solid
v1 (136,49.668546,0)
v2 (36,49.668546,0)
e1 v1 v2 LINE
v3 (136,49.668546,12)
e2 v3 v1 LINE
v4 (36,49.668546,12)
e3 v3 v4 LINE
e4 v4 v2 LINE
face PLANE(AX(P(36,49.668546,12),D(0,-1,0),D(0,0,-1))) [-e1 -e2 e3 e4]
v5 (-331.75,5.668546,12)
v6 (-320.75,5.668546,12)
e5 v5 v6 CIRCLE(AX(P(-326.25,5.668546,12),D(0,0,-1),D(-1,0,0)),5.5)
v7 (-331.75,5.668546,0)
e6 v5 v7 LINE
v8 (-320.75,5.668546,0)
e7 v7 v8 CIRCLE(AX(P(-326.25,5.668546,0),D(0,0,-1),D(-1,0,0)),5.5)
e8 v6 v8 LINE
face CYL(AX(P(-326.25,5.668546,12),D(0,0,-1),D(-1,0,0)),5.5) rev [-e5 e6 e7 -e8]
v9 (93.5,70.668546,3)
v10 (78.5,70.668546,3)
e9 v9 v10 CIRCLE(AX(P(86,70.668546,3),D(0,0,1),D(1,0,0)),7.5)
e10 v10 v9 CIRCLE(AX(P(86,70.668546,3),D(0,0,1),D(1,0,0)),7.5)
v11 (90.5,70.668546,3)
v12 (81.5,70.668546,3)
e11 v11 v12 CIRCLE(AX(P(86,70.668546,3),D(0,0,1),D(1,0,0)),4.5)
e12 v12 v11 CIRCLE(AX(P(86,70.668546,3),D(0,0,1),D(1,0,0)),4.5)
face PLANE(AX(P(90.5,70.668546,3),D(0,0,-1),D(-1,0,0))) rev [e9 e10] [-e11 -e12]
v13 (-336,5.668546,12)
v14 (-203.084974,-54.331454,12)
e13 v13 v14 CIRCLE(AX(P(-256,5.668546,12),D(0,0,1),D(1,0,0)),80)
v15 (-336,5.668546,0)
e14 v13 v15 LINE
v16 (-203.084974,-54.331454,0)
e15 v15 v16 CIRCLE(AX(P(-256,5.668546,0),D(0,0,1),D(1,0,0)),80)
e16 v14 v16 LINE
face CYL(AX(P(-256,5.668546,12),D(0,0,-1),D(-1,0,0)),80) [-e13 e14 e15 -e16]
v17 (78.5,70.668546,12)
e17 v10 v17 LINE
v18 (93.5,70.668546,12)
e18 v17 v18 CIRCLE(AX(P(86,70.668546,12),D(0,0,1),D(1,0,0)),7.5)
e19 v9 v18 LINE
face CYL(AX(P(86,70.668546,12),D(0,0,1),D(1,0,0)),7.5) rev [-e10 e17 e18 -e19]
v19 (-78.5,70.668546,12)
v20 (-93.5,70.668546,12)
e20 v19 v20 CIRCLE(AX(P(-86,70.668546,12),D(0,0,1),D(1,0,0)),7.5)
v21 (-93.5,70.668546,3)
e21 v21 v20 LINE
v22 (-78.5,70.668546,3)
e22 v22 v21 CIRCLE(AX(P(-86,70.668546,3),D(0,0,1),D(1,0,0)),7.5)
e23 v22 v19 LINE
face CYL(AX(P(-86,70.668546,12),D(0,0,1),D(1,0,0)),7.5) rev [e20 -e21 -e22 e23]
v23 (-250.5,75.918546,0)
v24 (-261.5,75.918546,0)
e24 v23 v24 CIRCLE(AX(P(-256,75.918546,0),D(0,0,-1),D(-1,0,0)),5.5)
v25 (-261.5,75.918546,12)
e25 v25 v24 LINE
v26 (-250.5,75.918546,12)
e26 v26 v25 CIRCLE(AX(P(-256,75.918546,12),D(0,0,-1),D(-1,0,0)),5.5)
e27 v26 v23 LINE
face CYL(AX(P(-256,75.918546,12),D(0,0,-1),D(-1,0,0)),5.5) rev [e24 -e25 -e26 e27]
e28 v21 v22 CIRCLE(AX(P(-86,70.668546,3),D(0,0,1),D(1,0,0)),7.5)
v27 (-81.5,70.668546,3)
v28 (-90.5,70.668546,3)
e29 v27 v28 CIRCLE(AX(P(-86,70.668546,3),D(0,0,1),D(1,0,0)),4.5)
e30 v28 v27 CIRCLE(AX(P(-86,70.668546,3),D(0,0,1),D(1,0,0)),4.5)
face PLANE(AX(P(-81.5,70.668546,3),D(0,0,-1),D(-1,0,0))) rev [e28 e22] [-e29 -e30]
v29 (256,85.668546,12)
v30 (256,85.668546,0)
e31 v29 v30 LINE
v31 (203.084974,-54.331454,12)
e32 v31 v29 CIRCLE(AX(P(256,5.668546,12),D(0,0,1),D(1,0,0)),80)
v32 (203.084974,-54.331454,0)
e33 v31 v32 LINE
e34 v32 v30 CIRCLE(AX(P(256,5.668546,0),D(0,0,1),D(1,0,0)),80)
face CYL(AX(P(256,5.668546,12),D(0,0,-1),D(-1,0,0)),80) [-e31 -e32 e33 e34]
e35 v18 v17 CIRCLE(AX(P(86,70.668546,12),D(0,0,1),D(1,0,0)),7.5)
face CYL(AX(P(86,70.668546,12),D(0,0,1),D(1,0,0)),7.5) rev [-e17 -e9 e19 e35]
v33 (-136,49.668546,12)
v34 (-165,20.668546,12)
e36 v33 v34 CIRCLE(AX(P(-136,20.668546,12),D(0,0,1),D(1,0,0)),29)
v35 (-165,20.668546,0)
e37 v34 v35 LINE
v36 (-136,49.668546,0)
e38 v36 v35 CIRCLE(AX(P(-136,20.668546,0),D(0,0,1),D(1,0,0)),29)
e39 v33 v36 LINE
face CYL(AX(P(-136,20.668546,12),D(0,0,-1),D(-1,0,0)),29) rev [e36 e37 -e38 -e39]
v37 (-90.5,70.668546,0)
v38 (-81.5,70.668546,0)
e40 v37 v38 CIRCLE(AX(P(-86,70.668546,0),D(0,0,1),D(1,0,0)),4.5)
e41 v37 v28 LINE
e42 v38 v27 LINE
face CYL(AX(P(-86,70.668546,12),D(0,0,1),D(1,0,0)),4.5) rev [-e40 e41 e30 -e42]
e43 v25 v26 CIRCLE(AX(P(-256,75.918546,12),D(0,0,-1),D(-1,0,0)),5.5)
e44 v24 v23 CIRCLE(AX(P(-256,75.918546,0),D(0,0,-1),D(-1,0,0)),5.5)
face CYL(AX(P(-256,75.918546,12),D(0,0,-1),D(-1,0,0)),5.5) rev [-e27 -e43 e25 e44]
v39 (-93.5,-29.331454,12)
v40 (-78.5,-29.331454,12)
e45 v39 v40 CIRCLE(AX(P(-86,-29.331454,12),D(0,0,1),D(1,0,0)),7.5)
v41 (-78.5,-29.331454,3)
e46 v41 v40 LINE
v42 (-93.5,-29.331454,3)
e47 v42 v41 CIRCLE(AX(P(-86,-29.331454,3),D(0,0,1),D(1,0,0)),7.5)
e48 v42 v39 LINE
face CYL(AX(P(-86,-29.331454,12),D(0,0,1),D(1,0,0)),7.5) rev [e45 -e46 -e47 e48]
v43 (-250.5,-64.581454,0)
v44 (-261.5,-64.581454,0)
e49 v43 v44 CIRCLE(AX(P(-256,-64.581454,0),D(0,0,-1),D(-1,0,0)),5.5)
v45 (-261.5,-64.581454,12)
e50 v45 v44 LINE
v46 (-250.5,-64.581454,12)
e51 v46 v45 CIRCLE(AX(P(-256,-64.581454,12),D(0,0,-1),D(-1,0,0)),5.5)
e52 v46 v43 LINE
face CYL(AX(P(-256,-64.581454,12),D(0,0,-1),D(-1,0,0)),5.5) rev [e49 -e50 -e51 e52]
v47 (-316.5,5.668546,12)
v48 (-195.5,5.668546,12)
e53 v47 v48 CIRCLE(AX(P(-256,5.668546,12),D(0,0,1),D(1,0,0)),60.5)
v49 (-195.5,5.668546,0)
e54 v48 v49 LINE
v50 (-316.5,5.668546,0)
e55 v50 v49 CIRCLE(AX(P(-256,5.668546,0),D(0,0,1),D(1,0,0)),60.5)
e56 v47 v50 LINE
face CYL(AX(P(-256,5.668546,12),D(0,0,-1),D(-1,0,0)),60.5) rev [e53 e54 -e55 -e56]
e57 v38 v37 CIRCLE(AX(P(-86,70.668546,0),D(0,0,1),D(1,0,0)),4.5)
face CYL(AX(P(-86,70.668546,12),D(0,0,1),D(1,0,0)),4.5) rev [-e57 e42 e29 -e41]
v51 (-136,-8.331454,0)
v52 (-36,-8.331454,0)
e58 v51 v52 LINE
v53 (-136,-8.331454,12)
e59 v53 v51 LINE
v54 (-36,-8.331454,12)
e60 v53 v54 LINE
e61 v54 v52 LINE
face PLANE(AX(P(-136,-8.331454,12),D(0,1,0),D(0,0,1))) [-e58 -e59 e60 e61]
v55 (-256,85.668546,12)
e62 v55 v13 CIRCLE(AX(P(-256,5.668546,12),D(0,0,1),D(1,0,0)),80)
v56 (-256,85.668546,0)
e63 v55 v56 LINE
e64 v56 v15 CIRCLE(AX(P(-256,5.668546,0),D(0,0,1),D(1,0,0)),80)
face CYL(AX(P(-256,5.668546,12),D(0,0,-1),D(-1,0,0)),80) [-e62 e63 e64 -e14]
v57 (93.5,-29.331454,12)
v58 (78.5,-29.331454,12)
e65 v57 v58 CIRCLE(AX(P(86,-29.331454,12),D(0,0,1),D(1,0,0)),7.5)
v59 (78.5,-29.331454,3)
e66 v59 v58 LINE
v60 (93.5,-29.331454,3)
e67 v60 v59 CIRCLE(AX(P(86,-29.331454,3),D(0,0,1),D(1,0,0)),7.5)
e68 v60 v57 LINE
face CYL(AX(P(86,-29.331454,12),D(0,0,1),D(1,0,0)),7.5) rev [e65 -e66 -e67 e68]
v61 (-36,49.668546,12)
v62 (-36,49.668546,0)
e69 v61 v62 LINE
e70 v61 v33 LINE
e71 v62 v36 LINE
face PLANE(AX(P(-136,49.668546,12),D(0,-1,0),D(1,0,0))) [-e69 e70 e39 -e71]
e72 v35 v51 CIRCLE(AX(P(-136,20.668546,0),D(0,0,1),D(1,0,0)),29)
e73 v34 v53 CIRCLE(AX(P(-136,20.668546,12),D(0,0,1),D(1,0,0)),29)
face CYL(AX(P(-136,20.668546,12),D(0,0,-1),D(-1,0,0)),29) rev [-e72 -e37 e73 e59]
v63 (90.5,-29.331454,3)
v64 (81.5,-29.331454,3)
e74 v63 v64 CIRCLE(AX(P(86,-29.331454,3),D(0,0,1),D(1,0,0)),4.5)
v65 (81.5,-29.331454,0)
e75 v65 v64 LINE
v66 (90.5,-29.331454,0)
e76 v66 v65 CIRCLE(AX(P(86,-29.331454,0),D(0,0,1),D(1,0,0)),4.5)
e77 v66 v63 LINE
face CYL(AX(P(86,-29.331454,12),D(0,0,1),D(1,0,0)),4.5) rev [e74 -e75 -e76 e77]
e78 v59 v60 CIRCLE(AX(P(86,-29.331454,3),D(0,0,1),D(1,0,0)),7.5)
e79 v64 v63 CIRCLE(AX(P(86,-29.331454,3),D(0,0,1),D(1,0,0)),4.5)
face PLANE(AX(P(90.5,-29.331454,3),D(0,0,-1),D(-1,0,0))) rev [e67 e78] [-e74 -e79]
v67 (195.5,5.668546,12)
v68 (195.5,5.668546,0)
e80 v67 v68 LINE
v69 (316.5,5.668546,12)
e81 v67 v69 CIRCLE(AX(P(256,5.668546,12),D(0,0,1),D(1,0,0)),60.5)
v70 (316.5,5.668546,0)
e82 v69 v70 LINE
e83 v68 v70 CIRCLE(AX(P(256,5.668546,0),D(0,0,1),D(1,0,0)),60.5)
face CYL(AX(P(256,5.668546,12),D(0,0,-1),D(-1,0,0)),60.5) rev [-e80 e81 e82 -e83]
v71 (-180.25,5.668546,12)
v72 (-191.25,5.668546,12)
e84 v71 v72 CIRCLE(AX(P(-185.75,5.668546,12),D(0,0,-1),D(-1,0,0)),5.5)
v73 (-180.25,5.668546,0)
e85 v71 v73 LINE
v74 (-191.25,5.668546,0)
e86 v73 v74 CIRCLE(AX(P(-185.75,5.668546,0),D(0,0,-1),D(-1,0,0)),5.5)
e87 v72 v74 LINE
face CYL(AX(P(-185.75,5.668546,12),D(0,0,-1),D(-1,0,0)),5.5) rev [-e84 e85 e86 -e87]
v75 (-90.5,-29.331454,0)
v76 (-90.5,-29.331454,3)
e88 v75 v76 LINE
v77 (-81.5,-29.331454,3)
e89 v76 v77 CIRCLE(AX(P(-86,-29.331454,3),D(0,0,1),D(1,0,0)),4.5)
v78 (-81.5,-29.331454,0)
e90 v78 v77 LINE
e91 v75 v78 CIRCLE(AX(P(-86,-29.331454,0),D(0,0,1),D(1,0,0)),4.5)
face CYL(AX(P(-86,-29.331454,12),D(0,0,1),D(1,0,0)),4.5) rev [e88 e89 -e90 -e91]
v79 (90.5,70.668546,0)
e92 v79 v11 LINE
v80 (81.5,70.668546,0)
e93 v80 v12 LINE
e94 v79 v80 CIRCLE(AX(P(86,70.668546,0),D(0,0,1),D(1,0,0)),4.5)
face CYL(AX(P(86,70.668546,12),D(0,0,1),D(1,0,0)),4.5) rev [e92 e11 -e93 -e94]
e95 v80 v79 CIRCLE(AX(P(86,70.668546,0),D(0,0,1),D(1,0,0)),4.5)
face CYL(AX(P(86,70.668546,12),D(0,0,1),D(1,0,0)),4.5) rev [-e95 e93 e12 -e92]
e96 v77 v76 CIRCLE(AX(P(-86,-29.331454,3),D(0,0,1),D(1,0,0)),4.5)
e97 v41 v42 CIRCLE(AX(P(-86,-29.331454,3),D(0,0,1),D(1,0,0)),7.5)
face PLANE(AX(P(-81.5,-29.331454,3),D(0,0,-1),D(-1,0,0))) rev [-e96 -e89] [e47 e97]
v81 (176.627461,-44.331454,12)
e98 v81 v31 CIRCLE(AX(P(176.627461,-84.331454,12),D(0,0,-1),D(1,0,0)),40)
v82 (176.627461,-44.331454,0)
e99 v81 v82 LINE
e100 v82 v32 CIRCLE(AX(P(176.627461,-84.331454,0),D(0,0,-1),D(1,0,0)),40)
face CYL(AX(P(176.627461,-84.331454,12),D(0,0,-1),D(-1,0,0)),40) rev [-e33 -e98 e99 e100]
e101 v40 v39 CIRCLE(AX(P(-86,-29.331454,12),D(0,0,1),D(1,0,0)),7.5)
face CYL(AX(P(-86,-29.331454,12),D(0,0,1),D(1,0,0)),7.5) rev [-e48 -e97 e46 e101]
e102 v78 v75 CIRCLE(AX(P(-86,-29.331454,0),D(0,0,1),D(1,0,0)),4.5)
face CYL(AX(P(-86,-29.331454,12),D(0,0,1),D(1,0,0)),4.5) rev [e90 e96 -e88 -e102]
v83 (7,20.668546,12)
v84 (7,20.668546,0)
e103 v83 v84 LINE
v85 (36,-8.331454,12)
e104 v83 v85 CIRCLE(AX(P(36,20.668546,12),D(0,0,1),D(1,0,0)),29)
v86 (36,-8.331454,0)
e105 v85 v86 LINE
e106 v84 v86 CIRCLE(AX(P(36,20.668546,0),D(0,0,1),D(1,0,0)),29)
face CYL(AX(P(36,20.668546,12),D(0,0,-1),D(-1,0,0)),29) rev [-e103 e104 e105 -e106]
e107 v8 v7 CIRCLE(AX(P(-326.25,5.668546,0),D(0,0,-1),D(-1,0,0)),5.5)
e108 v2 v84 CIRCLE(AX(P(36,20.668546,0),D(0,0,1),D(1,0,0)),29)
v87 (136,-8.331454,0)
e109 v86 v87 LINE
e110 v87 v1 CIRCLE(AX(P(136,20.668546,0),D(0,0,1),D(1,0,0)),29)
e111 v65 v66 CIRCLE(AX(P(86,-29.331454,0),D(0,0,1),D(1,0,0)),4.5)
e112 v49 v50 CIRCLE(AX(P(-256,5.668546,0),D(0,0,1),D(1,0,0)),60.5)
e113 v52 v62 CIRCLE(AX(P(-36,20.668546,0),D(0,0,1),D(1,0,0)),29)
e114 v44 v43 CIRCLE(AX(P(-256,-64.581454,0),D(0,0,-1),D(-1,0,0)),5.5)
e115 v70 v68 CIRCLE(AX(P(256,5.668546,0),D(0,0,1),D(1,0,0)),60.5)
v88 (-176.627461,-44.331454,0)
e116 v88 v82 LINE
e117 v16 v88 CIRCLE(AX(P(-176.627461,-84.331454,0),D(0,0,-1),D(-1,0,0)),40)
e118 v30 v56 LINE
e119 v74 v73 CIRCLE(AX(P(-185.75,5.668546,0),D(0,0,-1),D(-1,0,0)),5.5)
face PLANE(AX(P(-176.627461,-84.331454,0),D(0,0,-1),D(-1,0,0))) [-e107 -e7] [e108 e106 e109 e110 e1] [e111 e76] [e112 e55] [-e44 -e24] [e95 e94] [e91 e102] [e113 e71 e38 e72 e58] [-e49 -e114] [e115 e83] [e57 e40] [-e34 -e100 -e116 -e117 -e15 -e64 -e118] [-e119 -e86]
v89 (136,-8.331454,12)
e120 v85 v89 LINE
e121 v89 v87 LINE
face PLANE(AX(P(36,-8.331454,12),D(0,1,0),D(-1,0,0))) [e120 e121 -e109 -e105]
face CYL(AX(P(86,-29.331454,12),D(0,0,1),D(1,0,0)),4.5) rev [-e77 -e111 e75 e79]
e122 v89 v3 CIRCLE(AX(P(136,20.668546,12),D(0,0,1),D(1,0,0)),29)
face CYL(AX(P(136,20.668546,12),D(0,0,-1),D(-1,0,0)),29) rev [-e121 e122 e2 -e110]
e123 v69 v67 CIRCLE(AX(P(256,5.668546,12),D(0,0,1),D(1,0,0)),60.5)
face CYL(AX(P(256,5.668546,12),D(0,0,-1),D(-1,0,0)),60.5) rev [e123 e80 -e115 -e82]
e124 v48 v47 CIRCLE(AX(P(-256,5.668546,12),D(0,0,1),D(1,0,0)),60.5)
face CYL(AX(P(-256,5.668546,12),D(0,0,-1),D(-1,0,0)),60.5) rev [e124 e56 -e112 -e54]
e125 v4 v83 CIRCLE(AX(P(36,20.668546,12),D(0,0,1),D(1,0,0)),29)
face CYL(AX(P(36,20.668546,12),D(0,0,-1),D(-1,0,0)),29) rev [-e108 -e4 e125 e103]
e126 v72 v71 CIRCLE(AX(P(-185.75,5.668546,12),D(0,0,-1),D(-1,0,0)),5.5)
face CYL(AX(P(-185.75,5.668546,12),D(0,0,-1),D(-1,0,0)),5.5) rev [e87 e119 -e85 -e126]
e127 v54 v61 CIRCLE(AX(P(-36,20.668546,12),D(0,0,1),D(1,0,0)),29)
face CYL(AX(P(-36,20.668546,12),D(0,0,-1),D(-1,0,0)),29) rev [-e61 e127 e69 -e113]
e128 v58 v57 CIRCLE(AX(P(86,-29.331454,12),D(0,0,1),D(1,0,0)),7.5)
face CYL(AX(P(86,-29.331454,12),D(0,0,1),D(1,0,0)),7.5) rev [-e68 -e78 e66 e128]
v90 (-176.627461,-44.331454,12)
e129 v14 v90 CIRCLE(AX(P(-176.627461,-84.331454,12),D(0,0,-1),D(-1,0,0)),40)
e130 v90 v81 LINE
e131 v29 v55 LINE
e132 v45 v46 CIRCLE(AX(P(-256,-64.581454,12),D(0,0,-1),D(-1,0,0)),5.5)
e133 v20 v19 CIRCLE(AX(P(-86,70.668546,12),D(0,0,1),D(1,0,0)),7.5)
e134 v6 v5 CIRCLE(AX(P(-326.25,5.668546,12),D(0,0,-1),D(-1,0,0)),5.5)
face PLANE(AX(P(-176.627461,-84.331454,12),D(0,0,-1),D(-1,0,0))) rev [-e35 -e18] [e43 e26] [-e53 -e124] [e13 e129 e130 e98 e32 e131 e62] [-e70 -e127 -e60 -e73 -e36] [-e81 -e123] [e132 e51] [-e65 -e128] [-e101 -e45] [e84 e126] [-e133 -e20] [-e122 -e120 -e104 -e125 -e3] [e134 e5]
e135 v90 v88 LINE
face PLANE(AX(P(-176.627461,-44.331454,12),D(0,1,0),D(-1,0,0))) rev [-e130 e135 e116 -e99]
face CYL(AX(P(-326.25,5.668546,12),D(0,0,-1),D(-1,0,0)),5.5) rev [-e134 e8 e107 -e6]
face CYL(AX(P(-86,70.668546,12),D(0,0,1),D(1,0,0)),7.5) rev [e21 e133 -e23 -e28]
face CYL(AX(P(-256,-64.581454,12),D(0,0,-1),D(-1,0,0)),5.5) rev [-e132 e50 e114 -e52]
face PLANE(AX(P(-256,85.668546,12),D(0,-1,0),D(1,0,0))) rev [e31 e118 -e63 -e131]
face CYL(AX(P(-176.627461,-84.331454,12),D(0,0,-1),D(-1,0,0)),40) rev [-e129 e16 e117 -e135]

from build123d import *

# Parameters (mm, degrees)
SKETCH_1_R                   = 60.5
EXTRUDE_2_DEPTH              = 12
CUT_EXTRUDE_START            = 8
SKETCH_3_R                   = 60.5
CUT_EXTRUDE_2_DEPTH          = 339.956913315
SKETCH_5_R                   = 18
CUT_EXTRUDE_3_DEPTH          = 347.956913315
HOLE_WIZARD_M8_1_D           = 9
HOLE_WIZARD_M8_1_CBORE_D     = 15
HOLE_WIZARD_M8_1_CBORE_DEPTH = 9
SKETCH_9_R                   = 5.5
CUT_EXTRUDE_4_DEPTH          = 347.956913315
SKETCH_10_R                  = 60.5
CUT_EXTRUDE_5_DEPTH          = 347.841606064


with BuildPart() as part:
    # 草图1 → 凸台-拉伸2 (new body)
    with BuildSketch(Plane.XY):
        with BuildLine():
            Line((-256, 85.668545552), (256, 85.668545552))
            ThreePointArc((256, 85.668545552), (330.833147735, -22.615725695), (203.084973779, -54.331454448))
            ThreePointArc((203.084973779, -54.331454448), (190.769596292, -46.91488058), (176.627460668, -44.331454448))
            Line((176.627460668, -44.331454448), (-176.627460668, -44.331454448))
            ThreePointArc((-176.627460668, -44.331454448), (-190.769596292, -46.91488058), (-203.084973779, -54.331454448))
            ThreePointArc((-203.084973779, -54.331454448), (-330.833147735, -22.615725695), (-256, 85.668545552))
        make_face()
        with Locations((-256, 5.668545552)):
            Circle(SKETCH_1_R, mode=Mode.SUBTRACT)
        with BuildLine():
            Line((36, 49.668545552), (136, 49.668545552))
            ThreePointArc((136, 49.668545552), (165, 20.668545552), (136, -8.331454448))
            Line((136, -8.331454448), (36, -8.331454448))
            ThreePointArc((36, -8.331454448), (7, 20.668545552), (36, 49.668545552))
        make_face(mode=Mode.SUBTRACT)
        with BuildLine():
            Line((-136, 49.668545552), (-36, 49.668545552))
            ThreePointArc((-36, 49.668545552), (-7, 20.668545552), (-36, -8.331454448))
            Line((-36, -8.331454448), (-136, -8.331454448))
            ThreePointArc((-136, -8.331454448), (-165, 20.668545552), (-136, 49.668545552))
        make_face(mode=Mode.SUBTRACT)
    extrude(amount=EXTRUDE_2_DEPTH)

    # 草图3 → 切除-拉伸2 (cut, through all)
    with BuildSketch(Plane.XY.offset(CUT_EXTRUDE_START)):
        with Locations((256, 5.668545552)):
            Circle(SKETCH_3_R)
    extrude(amount=CUT_EXTRUDE_2_DEPTH, mode=Mode.SUBTRACT)

    # 草图5 → 切除-拉伸3 (cut, through all)
    with BuildSketch(Plane.XY):
        with Locations((256, 5.668545552)):
            Circle(SKETCH_5_R)
    extrude(amount=CUT_EXTRUDE_3_DEPTH, mode=Mode.SUBTRACT)

    # M8 六角圆柱头螺钉的柱形沉头孔1 (through all)
    with Locations(Plane.XY.offset(12)):
        with Locations((-86, 70.668545552), (-86, -29.331454448), (86, 70.668545552), (86, -29.331454448)):
            CounterBoreHole(HOLE_WIZARD_M8_1_D / 2, HOLE_WIZARD_M8_1_CBORE_D / 2, HOLE_WIZARD_M8_1_CBORE_DEPTH)

    # 草图9 → 切除-拉伸4 (cut, through all)
    with BuildSketch(Plane(origin=(0, 0, 0), x_dir=(-1, 0, 0), z_dir=(0, 0, -1))):
        with Locations((256, 75.918545552)):
            Circle(SKETCH_9_R)
        with Locations((326.25, 5.668545552)):
            Circle(SKETCH_9_R)
        with Locations((256, -64.581454448)):
            Circle(SKETCH_9_R)
        with Locations((185.75, 5.668545552)):
            Circle(SKETCH_9_R)
    extrude(amount=-CUT_EXTRUDE_4_DEPTH, mode=Mode.SUBTRACT)

    # 草图10 → 切除-拉伸5 (cut, through all)
    with BuildSketch(Plane.XY.offset(8)):
        with Locations((256, 5.668545552)):
            Circle(SKETCH_10_R)
    extrude(amount=-CUT_EXTRUDE_5_DEPTH, mode=Mode.SUBTRACT)


solid = part.part
